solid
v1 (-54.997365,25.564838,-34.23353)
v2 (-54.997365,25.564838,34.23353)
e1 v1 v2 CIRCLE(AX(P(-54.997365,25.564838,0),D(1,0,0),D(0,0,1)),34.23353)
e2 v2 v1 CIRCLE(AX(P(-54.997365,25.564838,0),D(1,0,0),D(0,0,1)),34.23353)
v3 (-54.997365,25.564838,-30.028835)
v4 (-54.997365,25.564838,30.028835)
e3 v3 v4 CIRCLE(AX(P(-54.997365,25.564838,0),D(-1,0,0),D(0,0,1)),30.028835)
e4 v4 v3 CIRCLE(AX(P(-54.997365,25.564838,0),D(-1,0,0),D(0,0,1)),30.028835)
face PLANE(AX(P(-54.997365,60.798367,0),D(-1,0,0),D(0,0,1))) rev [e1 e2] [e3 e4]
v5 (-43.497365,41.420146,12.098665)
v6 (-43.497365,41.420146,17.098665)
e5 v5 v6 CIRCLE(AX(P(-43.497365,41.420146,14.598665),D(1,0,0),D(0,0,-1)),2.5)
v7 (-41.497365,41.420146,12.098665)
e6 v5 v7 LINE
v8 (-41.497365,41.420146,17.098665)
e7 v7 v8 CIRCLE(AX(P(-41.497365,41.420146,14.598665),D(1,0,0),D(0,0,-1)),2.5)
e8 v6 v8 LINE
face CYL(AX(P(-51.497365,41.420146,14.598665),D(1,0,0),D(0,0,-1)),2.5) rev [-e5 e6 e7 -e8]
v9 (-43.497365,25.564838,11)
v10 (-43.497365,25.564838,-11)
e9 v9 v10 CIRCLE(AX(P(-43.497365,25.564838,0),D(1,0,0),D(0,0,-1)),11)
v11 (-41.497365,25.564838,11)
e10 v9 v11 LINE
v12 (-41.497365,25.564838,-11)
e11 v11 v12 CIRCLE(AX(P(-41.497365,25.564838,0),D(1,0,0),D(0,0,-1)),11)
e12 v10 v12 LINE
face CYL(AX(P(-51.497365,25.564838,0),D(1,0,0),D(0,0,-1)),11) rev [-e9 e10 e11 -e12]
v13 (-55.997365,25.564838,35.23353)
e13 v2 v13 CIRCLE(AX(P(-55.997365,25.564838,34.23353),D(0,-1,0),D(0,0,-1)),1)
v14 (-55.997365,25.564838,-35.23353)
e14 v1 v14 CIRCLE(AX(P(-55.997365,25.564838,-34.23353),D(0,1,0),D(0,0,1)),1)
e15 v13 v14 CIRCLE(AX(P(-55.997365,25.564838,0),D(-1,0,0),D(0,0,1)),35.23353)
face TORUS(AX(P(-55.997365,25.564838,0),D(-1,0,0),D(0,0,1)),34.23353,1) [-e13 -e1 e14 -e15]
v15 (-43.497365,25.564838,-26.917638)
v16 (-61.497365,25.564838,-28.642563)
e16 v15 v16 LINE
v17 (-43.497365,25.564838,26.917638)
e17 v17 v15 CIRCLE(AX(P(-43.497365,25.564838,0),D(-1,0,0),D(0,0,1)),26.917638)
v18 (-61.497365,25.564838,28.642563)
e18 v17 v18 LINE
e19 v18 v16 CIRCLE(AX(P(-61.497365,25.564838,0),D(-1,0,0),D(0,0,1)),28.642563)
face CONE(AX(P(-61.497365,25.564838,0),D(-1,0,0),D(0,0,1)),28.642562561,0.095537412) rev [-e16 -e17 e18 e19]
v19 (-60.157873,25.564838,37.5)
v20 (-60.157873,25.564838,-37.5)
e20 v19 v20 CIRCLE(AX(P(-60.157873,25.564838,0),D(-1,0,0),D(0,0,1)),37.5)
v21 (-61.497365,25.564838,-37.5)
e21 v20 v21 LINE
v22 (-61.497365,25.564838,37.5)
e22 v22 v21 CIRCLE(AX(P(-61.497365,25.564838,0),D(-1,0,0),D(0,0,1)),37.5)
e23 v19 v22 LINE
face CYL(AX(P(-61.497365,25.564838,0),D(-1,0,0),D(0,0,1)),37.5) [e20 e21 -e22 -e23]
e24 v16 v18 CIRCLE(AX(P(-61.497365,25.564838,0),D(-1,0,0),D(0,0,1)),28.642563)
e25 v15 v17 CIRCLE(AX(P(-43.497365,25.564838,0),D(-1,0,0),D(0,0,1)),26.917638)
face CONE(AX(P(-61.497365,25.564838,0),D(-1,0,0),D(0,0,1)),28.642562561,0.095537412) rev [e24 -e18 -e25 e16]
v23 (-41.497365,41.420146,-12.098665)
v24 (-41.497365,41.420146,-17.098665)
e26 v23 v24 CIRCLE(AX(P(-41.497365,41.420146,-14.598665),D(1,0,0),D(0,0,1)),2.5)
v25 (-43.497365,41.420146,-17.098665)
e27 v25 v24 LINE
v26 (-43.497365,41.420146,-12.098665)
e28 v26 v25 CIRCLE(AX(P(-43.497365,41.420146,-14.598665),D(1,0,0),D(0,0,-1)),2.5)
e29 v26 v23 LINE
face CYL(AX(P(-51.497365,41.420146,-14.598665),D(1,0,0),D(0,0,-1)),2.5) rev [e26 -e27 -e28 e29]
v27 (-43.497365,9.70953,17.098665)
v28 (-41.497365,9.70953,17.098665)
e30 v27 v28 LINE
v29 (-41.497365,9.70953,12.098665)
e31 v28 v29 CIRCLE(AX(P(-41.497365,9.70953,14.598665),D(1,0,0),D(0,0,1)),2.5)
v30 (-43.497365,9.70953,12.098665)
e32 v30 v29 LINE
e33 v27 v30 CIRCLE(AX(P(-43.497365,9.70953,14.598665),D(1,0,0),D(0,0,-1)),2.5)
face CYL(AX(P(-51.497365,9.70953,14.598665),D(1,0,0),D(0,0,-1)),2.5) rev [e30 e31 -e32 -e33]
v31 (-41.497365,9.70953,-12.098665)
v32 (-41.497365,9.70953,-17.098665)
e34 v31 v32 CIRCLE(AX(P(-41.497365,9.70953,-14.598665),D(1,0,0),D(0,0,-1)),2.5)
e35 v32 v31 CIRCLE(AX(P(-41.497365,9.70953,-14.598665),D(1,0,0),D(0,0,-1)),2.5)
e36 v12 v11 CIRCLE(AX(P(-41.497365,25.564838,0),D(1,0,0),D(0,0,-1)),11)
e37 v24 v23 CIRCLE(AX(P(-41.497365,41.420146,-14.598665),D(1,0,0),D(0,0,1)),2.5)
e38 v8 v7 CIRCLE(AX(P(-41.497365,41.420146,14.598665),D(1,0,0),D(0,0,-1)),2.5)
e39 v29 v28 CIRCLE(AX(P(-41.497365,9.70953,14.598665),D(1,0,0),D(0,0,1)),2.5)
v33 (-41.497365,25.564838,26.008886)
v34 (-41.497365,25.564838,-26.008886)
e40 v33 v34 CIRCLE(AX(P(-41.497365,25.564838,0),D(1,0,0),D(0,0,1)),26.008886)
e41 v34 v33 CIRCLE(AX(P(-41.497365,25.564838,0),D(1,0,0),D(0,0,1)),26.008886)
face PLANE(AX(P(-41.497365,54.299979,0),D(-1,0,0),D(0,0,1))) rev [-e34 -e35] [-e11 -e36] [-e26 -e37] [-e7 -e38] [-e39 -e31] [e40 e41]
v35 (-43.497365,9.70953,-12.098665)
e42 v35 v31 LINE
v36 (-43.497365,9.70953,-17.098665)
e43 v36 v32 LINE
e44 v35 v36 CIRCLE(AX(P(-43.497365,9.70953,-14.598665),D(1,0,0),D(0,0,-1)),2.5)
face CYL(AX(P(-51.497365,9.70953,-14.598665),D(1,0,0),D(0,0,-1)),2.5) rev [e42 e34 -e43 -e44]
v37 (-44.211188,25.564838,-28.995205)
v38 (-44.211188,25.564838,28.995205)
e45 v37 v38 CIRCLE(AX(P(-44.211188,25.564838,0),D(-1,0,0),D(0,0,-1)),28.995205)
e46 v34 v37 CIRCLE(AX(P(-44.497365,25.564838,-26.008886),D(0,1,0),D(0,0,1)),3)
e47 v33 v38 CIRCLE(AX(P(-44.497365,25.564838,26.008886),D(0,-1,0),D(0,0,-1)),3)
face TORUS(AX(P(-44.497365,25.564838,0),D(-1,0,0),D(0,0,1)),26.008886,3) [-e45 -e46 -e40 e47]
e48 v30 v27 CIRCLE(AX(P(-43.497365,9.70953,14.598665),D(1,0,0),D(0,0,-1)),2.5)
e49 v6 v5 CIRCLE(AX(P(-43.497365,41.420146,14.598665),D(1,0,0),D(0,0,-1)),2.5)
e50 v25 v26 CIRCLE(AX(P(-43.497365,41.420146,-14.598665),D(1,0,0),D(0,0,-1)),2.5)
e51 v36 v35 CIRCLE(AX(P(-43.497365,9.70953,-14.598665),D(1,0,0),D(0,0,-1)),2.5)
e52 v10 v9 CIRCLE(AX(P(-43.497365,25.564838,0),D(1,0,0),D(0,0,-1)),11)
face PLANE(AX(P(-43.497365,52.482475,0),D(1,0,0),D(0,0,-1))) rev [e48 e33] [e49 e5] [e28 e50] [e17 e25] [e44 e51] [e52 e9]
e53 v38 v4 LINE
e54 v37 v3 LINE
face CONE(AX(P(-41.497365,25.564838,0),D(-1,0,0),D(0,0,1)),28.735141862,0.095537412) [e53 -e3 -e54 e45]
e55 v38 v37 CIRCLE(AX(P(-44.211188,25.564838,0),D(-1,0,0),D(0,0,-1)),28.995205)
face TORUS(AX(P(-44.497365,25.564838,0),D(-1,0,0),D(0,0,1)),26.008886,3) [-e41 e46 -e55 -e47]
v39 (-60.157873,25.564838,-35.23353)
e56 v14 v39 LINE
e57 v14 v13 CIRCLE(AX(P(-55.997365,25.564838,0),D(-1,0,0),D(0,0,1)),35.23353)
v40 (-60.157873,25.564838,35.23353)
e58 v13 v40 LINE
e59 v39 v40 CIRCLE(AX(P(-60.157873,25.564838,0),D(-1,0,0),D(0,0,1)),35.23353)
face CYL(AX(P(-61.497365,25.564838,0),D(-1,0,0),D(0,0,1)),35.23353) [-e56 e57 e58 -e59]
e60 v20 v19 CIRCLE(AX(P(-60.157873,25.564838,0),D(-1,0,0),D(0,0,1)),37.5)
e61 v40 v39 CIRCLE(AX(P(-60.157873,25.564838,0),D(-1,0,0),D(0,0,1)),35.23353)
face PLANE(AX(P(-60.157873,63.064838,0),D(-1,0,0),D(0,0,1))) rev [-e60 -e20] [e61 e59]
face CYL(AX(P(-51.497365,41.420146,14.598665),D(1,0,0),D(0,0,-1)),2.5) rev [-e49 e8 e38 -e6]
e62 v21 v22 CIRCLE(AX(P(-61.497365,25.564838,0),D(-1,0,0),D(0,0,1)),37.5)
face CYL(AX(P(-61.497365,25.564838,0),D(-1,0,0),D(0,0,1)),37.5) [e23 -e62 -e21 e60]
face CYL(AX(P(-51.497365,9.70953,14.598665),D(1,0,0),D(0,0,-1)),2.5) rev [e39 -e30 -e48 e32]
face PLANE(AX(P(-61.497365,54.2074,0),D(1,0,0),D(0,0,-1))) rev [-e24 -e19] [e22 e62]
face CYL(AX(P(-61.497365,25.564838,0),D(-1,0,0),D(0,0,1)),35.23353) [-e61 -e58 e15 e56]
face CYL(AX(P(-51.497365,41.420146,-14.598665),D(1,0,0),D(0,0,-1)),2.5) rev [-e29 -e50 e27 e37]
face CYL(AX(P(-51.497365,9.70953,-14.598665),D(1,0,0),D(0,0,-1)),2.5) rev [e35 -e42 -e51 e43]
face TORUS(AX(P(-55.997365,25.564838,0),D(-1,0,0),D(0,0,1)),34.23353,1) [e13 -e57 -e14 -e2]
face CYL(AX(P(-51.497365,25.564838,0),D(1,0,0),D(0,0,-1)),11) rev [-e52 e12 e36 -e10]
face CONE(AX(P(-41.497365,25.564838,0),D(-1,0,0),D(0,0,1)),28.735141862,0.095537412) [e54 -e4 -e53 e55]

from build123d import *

# Parameters (mm, degrees)
SKETCH2_R          = 11
SKETCH2_R_2        = 2.5
CUT_EXTRUDE1_DEPTH = 10
FILLET1_R          = 3
FILLET2_R          = 1


with BuildPart() as part:
    # Sketch1 → Revolve1 (revolve)
    with BuildSketch(Plane.XY, mode=Mode.PRIVATE) as revolve1_sk:
        Polygon((-61.497364751, 54.207400123), (-61.497364751, 63.064837562), (-60.157873326, 63.064837562), (-60.157873326, 60.798367254), (-54.997364751, 60.798367254), (-54.997364751, 55.593672907), (-41.497364751, 54.299979424), (-41.497364751, 25.564837562), (-43.497364751, 25.564837562), (-43.497364751, 52.482475479), align=None)
    revolve(revolve1_sk.sketch.rotate(Axis((-61.497364751, 25.564837562, 0), (1, 0, 0)), 90), axis=Axis((-61.497364751, 25.564837562, 0), (1, 0, 0)))

    # Sketch2 → Cut-Extrude1 (cut)
    with BuildSketch(Plane(origin=(-41.497364751, 0, 0), x_dir=(0, 0, -1), z_dir=(1, 0, 0))):
        with Locations((0, 25.564837562)):
            Circle(SKETCH2_R)
        with Locations((-14.598664639, 41.420145509)):
            Circle(SKETCH2_R_2)
        with Locations((14.598664639, 41.420145509)):
            Circle(SKETCH2_R_2)
        with Locations((14.598664639, 9.709529615)):
            Circle(SKETCH2_R_2)
        with Locations((-14.598664639, 9.709529615)):
            Circle(SKETCH2_R_2)
    extrude(amount=-CUT_EXTRUDE1_DEPTH, mode=Mode.SUBTRACT)

    # Fillet1
    fillet1_edges = [part.edges().sort_by_distance(p)[0] for p in [
        (-41.497364751, 25.564837562, -28.735141862),
    ]]
    fillet(fillet1_edges, radius=FILLET1_R)

    # Fillet2
    fillet2_edges = [part.edges().sort_by_distance(p)[0] for p in [
        (-54.997364751, 25.564837562, -35.233529691),
    ]]
    fillet(fillet2_edges, radius=FILLET2_R)


solid = part.part
